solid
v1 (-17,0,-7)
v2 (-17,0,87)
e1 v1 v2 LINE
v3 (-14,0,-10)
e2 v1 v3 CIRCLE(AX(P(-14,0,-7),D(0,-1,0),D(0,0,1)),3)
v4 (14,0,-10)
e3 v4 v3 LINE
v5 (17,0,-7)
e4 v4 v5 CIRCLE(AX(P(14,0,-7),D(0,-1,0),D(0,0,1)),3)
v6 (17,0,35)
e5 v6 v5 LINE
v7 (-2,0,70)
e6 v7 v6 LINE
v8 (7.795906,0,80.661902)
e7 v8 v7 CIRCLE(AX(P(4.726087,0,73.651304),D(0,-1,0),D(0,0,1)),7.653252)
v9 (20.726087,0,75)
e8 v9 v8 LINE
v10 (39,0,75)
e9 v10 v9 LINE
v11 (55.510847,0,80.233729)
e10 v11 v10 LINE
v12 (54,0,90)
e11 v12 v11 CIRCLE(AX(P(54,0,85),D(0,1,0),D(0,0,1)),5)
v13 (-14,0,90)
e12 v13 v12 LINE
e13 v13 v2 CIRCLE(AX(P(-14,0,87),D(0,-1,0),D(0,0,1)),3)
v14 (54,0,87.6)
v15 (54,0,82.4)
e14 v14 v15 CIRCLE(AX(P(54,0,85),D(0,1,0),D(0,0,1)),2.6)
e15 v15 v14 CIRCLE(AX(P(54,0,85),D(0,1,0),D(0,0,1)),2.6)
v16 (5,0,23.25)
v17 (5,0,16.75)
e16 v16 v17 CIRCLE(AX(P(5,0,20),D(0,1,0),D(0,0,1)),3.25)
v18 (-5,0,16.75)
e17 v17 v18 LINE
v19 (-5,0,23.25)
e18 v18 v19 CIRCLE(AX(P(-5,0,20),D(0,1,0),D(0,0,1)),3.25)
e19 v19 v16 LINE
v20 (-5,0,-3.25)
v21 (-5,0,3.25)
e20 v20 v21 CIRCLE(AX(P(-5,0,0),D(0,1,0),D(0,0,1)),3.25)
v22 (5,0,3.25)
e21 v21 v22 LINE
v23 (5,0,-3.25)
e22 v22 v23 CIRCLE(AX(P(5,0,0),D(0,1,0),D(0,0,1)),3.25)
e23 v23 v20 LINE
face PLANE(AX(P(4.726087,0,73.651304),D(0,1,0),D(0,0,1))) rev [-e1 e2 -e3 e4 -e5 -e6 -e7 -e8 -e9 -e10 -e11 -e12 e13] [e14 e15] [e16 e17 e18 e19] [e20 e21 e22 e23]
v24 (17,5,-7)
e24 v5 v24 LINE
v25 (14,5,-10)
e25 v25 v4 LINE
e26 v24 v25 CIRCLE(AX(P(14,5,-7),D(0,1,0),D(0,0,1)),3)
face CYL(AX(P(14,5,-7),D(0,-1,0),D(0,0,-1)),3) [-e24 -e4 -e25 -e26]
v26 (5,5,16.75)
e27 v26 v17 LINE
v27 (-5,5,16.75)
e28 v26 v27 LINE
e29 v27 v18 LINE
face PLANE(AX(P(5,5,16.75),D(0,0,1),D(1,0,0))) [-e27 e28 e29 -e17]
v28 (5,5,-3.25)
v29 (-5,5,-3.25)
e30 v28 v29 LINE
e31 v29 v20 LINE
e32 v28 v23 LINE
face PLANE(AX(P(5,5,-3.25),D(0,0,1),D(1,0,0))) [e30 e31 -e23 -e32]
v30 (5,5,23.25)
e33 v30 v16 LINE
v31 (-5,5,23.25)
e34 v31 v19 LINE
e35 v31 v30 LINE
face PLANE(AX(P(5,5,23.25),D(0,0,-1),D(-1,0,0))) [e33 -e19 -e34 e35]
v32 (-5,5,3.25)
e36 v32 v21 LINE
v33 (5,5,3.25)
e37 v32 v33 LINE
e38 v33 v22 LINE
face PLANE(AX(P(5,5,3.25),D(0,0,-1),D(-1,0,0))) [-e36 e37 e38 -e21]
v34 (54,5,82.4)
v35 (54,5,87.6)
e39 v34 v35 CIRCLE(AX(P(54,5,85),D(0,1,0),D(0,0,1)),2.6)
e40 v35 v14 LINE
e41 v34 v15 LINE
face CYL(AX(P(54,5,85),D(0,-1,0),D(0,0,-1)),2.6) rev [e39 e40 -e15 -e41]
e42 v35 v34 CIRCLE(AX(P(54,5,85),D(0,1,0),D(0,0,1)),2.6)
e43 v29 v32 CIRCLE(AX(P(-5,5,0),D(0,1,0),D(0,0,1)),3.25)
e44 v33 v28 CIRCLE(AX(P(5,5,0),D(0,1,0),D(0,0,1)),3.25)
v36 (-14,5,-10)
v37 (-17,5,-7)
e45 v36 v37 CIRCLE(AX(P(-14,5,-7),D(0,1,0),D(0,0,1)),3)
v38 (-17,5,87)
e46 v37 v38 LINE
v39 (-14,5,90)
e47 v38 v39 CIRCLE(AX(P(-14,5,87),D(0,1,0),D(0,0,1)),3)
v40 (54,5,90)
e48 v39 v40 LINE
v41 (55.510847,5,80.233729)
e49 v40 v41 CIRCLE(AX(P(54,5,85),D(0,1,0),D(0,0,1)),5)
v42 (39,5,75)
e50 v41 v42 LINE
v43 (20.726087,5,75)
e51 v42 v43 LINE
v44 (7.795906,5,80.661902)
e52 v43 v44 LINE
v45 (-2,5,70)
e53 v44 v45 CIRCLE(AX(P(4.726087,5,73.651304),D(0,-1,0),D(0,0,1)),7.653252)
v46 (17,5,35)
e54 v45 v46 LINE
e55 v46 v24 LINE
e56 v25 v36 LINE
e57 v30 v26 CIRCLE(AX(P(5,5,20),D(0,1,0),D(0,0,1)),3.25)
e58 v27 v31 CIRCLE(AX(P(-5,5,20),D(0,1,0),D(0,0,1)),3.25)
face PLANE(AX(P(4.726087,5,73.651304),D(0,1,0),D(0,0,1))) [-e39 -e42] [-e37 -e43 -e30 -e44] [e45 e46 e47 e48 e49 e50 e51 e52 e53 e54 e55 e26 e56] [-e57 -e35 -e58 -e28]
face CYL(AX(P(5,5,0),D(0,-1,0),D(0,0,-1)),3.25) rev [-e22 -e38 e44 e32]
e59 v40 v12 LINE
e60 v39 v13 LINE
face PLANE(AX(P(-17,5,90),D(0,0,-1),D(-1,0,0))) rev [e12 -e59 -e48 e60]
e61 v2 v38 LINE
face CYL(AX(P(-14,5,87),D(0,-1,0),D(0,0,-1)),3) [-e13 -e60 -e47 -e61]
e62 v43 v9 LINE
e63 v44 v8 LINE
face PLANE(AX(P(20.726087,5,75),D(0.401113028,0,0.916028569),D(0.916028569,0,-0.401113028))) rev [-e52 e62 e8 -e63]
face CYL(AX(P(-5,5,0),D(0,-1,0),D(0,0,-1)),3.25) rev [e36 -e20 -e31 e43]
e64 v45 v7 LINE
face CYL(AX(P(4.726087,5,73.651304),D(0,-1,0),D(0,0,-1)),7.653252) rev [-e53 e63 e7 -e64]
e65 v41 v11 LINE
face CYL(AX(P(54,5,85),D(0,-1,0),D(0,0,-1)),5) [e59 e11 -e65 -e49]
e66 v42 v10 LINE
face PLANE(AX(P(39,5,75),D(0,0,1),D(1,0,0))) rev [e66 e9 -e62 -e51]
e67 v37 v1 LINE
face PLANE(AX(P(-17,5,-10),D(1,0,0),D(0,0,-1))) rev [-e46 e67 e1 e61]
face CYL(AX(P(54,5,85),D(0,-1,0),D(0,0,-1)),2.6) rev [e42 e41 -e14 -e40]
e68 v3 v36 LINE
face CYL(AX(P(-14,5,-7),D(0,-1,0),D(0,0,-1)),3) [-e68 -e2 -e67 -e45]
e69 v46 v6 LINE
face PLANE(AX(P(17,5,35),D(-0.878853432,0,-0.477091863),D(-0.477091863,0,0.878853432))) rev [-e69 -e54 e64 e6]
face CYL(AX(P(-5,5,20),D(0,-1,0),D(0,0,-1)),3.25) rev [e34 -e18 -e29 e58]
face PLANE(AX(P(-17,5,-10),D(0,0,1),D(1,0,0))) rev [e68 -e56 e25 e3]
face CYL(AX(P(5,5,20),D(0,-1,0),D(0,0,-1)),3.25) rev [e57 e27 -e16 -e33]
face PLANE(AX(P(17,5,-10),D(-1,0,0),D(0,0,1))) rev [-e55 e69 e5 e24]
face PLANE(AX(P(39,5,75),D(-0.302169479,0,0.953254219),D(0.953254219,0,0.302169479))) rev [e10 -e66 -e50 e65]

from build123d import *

# Parameters (mm, degrees)
SKETCH1_R           = 2.6
BOSS_EXTRUDE1_DEPTH = 5
FILLET1_R           = 3


with BuildPart() as part:
    # Sketch1 → Boss-Extrude1 (new body)
    with BuildSketch(Plane(origin=(0, 0, 0), x_dir=(1, 0, 0), z_dir=(0, 1, 0))):
        with BuildLine():
            Line((-17, 10), (-17, -90))
            Line((-17, -90), (54, -90))
            ThreePointArc((54, -90), (58.941222292, -85.764409749), (55.510847396, -80.233728906))
            Line((55.510847396, -80.233728906), (39, -75))
            Line((39, -75), (20.726086957, -75))
            Line((20.726086957, -75), (7.79590612, -80.661902004))
            ThreePointArc((7.79590612, -80.661902004), (-0.909612834, -78.829253465), (-2, -70))
            Line((-2, -70), (17, -35))
            Line((17, -35), (17, 10))
            Line((17, 10), (-17, 10))
        make_face()
        with Locations(Location((54, -85, 0), (0, 0, 270))):
            Circle(SKETCH1_R, mode=Mode.SUBTRACT)
        with BuildLine():
            Line((5, -3.25), (-5, -3.25))
            ThreePointArc((-5, -3.25), (-8.25, 0), (-5, 3.25))
            Line((-5, 3.25), (5, 3.25))
            ThreePointArc((5, 3.25), (8.25, 0), (5, -3.25))
        make_face(mode=Mode.SUBTRACT)
        with BuildLine():
            Line((5, -23.25), (-5, -23.25))
            ThreePointArc((-5, -23.25), (-8.25, -20), (-5, -16.75))
            Line((-5, -16.75), (5, -16.75))
            ThreePointArc((5, -16.75), (8.25, -20), (5, -23.25))
        make_face(mode=Mode.SUBTRACT)
    extrude(amount=BOSS_EXTRUDE1_DEPTH)

    # Fillet1
    fillet1_edges = [part.edges().sort_by_distance(p)[0] for p in [
        (17, 2.5, -10),
        (-17, 2.5, 90),
        (-17, 2.5, -10),
    ]]
    fillet(fillet1_edges, radius=FILLET1_R)


solid = part.part
